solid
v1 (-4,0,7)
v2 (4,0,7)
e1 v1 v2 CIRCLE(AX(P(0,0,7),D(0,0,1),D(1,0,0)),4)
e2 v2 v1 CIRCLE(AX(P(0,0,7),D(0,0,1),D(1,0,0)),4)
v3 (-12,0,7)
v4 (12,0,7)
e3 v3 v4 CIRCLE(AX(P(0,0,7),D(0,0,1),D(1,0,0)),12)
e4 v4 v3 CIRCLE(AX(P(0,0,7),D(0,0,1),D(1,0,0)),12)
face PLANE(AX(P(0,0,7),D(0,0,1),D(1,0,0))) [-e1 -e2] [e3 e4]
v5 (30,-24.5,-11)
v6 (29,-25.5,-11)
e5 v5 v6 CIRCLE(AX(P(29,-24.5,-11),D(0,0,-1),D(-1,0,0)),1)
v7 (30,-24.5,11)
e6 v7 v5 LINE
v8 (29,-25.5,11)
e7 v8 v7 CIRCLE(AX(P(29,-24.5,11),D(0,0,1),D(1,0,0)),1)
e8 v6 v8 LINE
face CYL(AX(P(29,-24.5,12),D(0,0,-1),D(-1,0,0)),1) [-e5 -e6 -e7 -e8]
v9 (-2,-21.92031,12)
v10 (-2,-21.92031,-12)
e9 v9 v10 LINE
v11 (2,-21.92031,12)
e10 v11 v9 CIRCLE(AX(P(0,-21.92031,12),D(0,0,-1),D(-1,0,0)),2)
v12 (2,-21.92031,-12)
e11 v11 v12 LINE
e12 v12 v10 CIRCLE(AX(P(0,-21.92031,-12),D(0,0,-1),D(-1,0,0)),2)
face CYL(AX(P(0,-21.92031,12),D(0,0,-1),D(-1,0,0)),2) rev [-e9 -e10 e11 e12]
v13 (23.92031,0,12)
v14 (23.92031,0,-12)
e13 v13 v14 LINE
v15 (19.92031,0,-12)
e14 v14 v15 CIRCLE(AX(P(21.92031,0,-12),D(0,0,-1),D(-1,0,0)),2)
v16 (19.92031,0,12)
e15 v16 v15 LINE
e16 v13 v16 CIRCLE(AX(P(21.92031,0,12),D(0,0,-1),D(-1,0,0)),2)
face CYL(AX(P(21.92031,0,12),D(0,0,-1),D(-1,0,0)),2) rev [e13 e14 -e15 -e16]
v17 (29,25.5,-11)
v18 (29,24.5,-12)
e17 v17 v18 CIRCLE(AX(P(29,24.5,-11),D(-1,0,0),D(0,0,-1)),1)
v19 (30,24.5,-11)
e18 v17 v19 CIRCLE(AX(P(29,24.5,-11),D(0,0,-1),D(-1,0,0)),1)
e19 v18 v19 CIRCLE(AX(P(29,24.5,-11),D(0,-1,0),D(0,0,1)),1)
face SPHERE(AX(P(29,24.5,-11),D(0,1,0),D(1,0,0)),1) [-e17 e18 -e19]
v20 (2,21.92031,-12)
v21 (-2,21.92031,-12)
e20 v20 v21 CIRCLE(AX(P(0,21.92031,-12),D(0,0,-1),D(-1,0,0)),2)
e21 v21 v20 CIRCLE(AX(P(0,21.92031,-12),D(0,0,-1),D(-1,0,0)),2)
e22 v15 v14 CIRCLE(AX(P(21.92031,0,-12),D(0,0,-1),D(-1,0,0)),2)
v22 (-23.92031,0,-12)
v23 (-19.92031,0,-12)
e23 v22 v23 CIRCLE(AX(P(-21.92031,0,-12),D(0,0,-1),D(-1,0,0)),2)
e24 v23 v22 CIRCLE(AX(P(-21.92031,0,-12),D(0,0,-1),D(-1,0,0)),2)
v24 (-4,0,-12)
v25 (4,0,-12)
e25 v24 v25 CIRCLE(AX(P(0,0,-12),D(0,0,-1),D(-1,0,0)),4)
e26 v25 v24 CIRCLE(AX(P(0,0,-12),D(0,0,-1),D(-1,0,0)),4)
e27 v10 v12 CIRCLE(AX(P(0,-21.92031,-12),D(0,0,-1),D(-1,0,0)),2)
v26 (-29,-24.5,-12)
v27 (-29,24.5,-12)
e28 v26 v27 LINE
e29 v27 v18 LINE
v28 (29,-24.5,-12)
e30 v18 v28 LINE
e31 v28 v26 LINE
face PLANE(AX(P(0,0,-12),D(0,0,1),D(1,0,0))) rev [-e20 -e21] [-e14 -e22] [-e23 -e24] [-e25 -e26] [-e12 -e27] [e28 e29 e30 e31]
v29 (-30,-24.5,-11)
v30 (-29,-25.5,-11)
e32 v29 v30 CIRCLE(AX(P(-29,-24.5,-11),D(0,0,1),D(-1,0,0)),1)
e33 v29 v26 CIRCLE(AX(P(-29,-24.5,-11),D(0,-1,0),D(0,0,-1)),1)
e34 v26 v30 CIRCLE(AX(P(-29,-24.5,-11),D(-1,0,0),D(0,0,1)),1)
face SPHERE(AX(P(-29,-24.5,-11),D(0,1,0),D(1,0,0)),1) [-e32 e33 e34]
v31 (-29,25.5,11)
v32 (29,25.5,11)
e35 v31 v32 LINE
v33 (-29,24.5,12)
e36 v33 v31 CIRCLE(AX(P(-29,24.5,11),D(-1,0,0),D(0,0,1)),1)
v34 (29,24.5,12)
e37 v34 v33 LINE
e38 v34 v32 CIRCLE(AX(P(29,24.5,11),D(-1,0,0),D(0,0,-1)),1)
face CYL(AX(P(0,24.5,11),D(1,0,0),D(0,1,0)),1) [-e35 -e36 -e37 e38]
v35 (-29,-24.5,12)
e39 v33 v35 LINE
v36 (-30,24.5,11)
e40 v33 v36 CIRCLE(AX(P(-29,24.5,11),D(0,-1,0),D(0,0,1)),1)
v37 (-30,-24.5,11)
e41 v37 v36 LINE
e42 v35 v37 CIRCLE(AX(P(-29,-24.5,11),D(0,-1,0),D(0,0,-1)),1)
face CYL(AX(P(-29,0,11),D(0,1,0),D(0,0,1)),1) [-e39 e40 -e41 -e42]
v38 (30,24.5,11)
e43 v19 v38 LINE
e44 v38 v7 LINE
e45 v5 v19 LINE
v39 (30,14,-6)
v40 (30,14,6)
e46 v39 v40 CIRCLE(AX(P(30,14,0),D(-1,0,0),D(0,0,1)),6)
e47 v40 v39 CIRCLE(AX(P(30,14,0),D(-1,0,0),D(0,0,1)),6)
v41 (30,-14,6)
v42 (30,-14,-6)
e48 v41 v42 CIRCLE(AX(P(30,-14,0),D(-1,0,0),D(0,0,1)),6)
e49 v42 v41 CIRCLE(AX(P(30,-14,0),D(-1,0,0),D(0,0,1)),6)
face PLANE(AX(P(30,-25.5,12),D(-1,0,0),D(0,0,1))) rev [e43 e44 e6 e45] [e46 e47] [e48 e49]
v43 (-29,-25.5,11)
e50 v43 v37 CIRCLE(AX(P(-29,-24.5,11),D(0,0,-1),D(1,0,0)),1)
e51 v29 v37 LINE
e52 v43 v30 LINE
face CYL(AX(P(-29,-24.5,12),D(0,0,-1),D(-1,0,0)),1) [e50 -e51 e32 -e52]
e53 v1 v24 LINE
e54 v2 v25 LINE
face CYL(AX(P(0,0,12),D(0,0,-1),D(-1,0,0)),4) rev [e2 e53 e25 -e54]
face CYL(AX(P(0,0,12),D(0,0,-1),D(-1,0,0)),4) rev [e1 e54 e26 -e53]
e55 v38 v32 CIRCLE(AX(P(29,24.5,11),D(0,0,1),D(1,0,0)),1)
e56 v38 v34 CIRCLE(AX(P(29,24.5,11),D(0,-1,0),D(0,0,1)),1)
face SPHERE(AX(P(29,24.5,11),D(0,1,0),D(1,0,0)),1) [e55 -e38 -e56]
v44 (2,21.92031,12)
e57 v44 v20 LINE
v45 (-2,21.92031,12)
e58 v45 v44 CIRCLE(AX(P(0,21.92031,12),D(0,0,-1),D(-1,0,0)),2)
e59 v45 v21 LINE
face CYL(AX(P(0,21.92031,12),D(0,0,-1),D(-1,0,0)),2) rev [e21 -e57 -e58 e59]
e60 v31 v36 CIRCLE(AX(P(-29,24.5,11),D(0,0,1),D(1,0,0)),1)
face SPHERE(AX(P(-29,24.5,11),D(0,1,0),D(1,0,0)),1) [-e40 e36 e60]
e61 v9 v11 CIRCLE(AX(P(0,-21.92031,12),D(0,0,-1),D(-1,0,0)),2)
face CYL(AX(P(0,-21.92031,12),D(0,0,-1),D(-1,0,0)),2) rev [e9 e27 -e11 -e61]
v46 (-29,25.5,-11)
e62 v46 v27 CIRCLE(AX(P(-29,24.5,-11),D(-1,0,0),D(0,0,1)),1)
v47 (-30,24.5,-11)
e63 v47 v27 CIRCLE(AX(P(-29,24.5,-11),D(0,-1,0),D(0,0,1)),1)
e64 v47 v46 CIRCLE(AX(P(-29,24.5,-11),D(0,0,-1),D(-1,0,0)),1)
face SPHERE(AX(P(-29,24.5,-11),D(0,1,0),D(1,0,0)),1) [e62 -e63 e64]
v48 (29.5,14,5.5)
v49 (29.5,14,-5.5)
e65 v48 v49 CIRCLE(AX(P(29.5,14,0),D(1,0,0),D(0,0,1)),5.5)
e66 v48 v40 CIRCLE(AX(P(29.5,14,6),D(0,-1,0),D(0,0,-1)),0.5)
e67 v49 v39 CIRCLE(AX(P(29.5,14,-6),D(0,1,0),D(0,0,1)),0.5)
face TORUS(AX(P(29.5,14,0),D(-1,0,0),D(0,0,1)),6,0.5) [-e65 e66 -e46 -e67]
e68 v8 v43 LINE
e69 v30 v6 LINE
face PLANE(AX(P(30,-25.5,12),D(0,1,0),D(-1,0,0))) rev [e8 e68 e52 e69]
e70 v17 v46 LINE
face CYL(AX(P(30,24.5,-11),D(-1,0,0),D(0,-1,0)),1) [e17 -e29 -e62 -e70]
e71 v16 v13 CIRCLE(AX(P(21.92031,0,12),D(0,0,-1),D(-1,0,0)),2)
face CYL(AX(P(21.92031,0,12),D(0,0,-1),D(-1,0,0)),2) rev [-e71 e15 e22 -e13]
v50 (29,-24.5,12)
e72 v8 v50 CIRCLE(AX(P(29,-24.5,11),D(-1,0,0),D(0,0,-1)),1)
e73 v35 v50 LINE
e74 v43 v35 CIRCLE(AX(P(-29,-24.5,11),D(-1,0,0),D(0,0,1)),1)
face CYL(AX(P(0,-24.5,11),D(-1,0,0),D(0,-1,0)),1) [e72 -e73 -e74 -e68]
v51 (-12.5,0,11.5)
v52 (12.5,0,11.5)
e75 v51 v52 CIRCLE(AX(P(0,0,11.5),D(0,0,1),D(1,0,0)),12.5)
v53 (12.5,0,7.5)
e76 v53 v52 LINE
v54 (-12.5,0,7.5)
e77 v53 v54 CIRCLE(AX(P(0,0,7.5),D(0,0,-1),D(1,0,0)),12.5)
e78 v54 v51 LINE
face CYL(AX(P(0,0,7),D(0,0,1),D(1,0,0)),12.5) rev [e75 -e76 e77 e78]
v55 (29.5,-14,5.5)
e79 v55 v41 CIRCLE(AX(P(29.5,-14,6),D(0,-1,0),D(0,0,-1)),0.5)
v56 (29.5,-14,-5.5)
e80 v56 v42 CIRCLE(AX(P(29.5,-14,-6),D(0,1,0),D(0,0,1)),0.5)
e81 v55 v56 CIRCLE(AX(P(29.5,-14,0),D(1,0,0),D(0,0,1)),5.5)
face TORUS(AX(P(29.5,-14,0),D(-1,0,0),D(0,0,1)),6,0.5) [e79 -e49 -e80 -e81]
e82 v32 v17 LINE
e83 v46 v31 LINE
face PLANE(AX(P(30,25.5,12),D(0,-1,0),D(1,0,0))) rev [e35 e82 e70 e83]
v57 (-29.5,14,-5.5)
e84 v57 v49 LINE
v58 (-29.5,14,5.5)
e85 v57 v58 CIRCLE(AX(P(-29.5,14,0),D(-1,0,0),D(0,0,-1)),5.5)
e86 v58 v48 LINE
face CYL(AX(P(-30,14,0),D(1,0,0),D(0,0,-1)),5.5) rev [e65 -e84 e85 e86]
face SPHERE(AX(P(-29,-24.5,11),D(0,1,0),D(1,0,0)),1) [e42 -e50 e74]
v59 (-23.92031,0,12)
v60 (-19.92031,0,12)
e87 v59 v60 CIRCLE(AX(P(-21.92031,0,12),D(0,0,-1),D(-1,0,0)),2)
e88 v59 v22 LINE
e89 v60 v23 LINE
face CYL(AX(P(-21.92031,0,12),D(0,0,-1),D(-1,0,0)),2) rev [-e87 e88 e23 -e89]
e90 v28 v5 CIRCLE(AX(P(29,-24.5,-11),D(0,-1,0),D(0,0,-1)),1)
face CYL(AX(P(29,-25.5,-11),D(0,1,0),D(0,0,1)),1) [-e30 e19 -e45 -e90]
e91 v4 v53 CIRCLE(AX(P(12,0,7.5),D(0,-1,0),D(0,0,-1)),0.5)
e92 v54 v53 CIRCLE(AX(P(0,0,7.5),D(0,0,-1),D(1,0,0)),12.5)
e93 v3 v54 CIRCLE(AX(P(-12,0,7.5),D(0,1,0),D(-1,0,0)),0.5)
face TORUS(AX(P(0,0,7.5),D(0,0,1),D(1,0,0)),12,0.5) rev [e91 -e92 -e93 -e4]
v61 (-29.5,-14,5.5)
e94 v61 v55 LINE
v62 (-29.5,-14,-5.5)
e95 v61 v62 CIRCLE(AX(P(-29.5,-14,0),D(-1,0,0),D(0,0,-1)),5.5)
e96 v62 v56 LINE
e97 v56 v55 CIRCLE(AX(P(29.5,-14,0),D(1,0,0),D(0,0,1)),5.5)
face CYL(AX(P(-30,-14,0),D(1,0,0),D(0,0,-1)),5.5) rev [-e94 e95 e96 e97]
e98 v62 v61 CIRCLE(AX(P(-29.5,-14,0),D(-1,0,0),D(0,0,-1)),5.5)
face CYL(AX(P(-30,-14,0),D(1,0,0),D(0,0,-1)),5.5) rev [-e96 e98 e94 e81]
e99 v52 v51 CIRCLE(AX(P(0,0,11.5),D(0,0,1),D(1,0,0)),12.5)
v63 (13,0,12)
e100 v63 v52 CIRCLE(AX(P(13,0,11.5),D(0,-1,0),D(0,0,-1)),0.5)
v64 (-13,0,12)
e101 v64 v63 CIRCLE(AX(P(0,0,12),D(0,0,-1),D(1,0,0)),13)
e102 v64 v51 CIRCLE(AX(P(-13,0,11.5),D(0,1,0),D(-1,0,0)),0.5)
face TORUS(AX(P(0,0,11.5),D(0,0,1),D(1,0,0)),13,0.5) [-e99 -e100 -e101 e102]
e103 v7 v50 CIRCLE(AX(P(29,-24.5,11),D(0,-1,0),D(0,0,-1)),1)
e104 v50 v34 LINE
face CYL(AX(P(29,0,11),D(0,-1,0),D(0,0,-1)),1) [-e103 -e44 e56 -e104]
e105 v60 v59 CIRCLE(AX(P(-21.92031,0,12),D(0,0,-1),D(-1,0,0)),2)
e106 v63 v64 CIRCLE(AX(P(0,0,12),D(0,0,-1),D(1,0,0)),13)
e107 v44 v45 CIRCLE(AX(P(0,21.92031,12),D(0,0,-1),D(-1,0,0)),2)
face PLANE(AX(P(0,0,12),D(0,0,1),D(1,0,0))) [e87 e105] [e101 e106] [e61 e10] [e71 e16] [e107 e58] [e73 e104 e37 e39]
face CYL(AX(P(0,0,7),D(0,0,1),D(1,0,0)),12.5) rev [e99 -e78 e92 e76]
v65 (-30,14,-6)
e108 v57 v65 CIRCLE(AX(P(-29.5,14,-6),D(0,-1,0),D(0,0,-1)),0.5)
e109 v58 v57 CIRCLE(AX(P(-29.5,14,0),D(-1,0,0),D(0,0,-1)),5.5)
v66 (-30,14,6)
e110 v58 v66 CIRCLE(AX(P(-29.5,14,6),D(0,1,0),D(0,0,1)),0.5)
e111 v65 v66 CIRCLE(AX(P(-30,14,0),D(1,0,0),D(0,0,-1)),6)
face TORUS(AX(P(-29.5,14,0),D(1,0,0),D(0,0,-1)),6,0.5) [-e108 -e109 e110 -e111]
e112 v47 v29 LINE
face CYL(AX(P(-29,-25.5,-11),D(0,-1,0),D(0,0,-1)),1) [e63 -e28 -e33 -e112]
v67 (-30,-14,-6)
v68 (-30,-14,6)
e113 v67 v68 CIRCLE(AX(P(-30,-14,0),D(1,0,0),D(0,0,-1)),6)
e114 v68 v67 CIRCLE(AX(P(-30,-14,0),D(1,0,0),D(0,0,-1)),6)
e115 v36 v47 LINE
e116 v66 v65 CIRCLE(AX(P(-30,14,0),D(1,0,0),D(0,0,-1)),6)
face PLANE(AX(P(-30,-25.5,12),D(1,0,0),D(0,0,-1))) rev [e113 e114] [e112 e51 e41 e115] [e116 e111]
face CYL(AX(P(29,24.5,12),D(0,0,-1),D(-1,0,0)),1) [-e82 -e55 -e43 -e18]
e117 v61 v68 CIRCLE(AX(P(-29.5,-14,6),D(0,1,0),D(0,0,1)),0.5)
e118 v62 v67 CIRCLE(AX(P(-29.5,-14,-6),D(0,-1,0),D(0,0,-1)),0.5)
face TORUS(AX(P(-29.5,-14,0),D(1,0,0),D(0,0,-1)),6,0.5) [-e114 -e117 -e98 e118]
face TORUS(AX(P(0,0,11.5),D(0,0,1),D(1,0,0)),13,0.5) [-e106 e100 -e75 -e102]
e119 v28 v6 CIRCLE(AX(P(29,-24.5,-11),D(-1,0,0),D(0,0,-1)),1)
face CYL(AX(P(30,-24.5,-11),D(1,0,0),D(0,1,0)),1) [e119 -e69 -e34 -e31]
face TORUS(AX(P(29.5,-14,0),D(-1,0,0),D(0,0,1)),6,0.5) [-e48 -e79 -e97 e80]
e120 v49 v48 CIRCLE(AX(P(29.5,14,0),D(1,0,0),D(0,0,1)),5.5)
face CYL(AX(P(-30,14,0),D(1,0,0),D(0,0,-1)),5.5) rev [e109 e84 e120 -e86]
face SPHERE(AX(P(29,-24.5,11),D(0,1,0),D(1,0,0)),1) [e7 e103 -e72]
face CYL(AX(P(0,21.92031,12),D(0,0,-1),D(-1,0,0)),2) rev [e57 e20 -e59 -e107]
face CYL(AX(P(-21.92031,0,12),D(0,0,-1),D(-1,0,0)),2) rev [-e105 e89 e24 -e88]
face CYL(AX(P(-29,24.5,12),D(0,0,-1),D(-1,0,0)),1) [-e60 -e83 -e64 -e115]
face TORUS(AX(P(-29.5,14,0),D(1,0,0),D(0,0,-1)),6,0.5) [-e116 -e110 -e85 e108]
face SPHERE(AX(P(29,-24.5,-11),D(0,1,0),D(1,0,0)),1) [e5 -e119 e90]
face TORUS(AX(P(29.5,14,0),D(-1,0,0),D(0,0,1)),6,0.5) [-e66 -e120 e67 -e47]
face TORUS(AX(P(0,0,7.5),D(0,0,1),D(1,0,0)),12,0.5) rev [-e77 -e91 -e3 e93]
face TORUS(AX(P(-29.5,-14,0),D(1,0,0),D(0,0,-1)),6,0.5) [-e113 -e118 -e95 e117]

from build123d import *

# Parameters (mm, degrees)
SKETCH1_W           = 60
SKETCH1_H           = 51
BOSS_EXTRUDE1_DEPTH = 12
SKETCH2_R           = 12.5
CUT_EXTRUDE1_DEPTH  = 5
SKETCH3_R           = 5.5
CUT_EXTRUDE2_DEPTH  = 67.289139382
FILLET1_R           = 1
FILLET2_R           = 0.5
SKETCH4_R           = 4
CUT_EXTRUDE3_DEPTH  = 47.111278447
SKETCH5_R           = 2
CUT_EXTRUDE5_DEPTH  = 47.111278447


with BuildPart() as part:
    # Sketch1 → Boss-Extrude1 (new, symmetric)
    with BuildSketch(Plane.XY):
        Rectangle(SKETCH1_W, SKETCH1_H)
    extrude(amount=BOSS_EXTRUDE1_DEPTH, both=True)

    # Sketch2 → Cut-Extrude1 (cut)
    with BuildSketch(Plane.XY.offset(12)):
        Circle(SKETCH2_R)
    extrude(amount=-CUT_EXTRUDE1_DEPTH, mode=Mode.SUBTRACT)

    # Sketch3 → Cut-Extrude2 (cut, through all)
    with BuildSketch(Plane(origin=(30, 0, 0), x_dir=(0, 0, -1), z_dir=(1, 0, 0))):
        with Locations((0, 14)):
            Circle(SKETCH3_R)
        with Locations((0, -14)):
            Circle(SKETCH3_R)
    extrude(amount=-CUT_EXTRUDE2_DEPTH, mode=Mode.SUBTRACT)

    # Fillet1
    fillet1_edges = [part.edges().sort_by_distance(p)[0] for p in [
        (30, 0, 12),
        (0, 25.5, 12),
        (-30, 0, 12),
        (0, 25.5, -12),
        (30, 0, -12),
        (0, -25.5, -12),
        (-30, 0, -12),
        (0, -25.5, 12),
        (-30, 25.5, 0),
        (30, 25.5, 0),
        (30, -25.5, 0),
        (-30, -25.5, 0),
    ]]
    fillet(fillet1_edges, radius=FILLET1_R)

    # Fillet2
    fillet2_edges = [part.edges().sort_by_distance(p)[0] for p in [
        (-12.5, 0, 7),
        (-12.5, 0, 12),
        (-30, 14, 5.5),
        (30, 14, 5.5),
        (-30, -14, 5.5),
        (30, -14, 5.5),
    ]]
    fillet(fillet2_edges, radius=FILLET2_R)

    # Sketch4 → Cut-Extrude3 (cut, through all)
    with BuildSketch(Plane(origin=(0, 0, -12), x_dir=(-1, 0, 0), z_dir=(0, 0, -1))):
        Circle(SKETCH4_R)
    extrude(amount=-CUT_EXTRUDE3_DEPTH, mode=Mode.SUBTRACT)

    # Sketch5 → Cut-Extrude5 (cut, through all)
    with BuildSketch(Plane(origin=(0, 0, -12), x_dir=(-1, 0, 0), z_dir=(0, 0, -1))):
        with Locations((0, -21.920310217)):
            Circle(SKETCH5_R)
        with Locations((-21.920310217, 0)):
            Circle(SKETCH5_R)
        with Locations((0, 21.920310217)):
            Circle(SKETCH5_R)
        with Locations((21.920310217, 0)):
            Circle(SKETCH5_R)
    extrude(amount=-CUT_EXTRUDE5_DEPTH, mode=Mode.SUBTRACT)


solid = part.part
